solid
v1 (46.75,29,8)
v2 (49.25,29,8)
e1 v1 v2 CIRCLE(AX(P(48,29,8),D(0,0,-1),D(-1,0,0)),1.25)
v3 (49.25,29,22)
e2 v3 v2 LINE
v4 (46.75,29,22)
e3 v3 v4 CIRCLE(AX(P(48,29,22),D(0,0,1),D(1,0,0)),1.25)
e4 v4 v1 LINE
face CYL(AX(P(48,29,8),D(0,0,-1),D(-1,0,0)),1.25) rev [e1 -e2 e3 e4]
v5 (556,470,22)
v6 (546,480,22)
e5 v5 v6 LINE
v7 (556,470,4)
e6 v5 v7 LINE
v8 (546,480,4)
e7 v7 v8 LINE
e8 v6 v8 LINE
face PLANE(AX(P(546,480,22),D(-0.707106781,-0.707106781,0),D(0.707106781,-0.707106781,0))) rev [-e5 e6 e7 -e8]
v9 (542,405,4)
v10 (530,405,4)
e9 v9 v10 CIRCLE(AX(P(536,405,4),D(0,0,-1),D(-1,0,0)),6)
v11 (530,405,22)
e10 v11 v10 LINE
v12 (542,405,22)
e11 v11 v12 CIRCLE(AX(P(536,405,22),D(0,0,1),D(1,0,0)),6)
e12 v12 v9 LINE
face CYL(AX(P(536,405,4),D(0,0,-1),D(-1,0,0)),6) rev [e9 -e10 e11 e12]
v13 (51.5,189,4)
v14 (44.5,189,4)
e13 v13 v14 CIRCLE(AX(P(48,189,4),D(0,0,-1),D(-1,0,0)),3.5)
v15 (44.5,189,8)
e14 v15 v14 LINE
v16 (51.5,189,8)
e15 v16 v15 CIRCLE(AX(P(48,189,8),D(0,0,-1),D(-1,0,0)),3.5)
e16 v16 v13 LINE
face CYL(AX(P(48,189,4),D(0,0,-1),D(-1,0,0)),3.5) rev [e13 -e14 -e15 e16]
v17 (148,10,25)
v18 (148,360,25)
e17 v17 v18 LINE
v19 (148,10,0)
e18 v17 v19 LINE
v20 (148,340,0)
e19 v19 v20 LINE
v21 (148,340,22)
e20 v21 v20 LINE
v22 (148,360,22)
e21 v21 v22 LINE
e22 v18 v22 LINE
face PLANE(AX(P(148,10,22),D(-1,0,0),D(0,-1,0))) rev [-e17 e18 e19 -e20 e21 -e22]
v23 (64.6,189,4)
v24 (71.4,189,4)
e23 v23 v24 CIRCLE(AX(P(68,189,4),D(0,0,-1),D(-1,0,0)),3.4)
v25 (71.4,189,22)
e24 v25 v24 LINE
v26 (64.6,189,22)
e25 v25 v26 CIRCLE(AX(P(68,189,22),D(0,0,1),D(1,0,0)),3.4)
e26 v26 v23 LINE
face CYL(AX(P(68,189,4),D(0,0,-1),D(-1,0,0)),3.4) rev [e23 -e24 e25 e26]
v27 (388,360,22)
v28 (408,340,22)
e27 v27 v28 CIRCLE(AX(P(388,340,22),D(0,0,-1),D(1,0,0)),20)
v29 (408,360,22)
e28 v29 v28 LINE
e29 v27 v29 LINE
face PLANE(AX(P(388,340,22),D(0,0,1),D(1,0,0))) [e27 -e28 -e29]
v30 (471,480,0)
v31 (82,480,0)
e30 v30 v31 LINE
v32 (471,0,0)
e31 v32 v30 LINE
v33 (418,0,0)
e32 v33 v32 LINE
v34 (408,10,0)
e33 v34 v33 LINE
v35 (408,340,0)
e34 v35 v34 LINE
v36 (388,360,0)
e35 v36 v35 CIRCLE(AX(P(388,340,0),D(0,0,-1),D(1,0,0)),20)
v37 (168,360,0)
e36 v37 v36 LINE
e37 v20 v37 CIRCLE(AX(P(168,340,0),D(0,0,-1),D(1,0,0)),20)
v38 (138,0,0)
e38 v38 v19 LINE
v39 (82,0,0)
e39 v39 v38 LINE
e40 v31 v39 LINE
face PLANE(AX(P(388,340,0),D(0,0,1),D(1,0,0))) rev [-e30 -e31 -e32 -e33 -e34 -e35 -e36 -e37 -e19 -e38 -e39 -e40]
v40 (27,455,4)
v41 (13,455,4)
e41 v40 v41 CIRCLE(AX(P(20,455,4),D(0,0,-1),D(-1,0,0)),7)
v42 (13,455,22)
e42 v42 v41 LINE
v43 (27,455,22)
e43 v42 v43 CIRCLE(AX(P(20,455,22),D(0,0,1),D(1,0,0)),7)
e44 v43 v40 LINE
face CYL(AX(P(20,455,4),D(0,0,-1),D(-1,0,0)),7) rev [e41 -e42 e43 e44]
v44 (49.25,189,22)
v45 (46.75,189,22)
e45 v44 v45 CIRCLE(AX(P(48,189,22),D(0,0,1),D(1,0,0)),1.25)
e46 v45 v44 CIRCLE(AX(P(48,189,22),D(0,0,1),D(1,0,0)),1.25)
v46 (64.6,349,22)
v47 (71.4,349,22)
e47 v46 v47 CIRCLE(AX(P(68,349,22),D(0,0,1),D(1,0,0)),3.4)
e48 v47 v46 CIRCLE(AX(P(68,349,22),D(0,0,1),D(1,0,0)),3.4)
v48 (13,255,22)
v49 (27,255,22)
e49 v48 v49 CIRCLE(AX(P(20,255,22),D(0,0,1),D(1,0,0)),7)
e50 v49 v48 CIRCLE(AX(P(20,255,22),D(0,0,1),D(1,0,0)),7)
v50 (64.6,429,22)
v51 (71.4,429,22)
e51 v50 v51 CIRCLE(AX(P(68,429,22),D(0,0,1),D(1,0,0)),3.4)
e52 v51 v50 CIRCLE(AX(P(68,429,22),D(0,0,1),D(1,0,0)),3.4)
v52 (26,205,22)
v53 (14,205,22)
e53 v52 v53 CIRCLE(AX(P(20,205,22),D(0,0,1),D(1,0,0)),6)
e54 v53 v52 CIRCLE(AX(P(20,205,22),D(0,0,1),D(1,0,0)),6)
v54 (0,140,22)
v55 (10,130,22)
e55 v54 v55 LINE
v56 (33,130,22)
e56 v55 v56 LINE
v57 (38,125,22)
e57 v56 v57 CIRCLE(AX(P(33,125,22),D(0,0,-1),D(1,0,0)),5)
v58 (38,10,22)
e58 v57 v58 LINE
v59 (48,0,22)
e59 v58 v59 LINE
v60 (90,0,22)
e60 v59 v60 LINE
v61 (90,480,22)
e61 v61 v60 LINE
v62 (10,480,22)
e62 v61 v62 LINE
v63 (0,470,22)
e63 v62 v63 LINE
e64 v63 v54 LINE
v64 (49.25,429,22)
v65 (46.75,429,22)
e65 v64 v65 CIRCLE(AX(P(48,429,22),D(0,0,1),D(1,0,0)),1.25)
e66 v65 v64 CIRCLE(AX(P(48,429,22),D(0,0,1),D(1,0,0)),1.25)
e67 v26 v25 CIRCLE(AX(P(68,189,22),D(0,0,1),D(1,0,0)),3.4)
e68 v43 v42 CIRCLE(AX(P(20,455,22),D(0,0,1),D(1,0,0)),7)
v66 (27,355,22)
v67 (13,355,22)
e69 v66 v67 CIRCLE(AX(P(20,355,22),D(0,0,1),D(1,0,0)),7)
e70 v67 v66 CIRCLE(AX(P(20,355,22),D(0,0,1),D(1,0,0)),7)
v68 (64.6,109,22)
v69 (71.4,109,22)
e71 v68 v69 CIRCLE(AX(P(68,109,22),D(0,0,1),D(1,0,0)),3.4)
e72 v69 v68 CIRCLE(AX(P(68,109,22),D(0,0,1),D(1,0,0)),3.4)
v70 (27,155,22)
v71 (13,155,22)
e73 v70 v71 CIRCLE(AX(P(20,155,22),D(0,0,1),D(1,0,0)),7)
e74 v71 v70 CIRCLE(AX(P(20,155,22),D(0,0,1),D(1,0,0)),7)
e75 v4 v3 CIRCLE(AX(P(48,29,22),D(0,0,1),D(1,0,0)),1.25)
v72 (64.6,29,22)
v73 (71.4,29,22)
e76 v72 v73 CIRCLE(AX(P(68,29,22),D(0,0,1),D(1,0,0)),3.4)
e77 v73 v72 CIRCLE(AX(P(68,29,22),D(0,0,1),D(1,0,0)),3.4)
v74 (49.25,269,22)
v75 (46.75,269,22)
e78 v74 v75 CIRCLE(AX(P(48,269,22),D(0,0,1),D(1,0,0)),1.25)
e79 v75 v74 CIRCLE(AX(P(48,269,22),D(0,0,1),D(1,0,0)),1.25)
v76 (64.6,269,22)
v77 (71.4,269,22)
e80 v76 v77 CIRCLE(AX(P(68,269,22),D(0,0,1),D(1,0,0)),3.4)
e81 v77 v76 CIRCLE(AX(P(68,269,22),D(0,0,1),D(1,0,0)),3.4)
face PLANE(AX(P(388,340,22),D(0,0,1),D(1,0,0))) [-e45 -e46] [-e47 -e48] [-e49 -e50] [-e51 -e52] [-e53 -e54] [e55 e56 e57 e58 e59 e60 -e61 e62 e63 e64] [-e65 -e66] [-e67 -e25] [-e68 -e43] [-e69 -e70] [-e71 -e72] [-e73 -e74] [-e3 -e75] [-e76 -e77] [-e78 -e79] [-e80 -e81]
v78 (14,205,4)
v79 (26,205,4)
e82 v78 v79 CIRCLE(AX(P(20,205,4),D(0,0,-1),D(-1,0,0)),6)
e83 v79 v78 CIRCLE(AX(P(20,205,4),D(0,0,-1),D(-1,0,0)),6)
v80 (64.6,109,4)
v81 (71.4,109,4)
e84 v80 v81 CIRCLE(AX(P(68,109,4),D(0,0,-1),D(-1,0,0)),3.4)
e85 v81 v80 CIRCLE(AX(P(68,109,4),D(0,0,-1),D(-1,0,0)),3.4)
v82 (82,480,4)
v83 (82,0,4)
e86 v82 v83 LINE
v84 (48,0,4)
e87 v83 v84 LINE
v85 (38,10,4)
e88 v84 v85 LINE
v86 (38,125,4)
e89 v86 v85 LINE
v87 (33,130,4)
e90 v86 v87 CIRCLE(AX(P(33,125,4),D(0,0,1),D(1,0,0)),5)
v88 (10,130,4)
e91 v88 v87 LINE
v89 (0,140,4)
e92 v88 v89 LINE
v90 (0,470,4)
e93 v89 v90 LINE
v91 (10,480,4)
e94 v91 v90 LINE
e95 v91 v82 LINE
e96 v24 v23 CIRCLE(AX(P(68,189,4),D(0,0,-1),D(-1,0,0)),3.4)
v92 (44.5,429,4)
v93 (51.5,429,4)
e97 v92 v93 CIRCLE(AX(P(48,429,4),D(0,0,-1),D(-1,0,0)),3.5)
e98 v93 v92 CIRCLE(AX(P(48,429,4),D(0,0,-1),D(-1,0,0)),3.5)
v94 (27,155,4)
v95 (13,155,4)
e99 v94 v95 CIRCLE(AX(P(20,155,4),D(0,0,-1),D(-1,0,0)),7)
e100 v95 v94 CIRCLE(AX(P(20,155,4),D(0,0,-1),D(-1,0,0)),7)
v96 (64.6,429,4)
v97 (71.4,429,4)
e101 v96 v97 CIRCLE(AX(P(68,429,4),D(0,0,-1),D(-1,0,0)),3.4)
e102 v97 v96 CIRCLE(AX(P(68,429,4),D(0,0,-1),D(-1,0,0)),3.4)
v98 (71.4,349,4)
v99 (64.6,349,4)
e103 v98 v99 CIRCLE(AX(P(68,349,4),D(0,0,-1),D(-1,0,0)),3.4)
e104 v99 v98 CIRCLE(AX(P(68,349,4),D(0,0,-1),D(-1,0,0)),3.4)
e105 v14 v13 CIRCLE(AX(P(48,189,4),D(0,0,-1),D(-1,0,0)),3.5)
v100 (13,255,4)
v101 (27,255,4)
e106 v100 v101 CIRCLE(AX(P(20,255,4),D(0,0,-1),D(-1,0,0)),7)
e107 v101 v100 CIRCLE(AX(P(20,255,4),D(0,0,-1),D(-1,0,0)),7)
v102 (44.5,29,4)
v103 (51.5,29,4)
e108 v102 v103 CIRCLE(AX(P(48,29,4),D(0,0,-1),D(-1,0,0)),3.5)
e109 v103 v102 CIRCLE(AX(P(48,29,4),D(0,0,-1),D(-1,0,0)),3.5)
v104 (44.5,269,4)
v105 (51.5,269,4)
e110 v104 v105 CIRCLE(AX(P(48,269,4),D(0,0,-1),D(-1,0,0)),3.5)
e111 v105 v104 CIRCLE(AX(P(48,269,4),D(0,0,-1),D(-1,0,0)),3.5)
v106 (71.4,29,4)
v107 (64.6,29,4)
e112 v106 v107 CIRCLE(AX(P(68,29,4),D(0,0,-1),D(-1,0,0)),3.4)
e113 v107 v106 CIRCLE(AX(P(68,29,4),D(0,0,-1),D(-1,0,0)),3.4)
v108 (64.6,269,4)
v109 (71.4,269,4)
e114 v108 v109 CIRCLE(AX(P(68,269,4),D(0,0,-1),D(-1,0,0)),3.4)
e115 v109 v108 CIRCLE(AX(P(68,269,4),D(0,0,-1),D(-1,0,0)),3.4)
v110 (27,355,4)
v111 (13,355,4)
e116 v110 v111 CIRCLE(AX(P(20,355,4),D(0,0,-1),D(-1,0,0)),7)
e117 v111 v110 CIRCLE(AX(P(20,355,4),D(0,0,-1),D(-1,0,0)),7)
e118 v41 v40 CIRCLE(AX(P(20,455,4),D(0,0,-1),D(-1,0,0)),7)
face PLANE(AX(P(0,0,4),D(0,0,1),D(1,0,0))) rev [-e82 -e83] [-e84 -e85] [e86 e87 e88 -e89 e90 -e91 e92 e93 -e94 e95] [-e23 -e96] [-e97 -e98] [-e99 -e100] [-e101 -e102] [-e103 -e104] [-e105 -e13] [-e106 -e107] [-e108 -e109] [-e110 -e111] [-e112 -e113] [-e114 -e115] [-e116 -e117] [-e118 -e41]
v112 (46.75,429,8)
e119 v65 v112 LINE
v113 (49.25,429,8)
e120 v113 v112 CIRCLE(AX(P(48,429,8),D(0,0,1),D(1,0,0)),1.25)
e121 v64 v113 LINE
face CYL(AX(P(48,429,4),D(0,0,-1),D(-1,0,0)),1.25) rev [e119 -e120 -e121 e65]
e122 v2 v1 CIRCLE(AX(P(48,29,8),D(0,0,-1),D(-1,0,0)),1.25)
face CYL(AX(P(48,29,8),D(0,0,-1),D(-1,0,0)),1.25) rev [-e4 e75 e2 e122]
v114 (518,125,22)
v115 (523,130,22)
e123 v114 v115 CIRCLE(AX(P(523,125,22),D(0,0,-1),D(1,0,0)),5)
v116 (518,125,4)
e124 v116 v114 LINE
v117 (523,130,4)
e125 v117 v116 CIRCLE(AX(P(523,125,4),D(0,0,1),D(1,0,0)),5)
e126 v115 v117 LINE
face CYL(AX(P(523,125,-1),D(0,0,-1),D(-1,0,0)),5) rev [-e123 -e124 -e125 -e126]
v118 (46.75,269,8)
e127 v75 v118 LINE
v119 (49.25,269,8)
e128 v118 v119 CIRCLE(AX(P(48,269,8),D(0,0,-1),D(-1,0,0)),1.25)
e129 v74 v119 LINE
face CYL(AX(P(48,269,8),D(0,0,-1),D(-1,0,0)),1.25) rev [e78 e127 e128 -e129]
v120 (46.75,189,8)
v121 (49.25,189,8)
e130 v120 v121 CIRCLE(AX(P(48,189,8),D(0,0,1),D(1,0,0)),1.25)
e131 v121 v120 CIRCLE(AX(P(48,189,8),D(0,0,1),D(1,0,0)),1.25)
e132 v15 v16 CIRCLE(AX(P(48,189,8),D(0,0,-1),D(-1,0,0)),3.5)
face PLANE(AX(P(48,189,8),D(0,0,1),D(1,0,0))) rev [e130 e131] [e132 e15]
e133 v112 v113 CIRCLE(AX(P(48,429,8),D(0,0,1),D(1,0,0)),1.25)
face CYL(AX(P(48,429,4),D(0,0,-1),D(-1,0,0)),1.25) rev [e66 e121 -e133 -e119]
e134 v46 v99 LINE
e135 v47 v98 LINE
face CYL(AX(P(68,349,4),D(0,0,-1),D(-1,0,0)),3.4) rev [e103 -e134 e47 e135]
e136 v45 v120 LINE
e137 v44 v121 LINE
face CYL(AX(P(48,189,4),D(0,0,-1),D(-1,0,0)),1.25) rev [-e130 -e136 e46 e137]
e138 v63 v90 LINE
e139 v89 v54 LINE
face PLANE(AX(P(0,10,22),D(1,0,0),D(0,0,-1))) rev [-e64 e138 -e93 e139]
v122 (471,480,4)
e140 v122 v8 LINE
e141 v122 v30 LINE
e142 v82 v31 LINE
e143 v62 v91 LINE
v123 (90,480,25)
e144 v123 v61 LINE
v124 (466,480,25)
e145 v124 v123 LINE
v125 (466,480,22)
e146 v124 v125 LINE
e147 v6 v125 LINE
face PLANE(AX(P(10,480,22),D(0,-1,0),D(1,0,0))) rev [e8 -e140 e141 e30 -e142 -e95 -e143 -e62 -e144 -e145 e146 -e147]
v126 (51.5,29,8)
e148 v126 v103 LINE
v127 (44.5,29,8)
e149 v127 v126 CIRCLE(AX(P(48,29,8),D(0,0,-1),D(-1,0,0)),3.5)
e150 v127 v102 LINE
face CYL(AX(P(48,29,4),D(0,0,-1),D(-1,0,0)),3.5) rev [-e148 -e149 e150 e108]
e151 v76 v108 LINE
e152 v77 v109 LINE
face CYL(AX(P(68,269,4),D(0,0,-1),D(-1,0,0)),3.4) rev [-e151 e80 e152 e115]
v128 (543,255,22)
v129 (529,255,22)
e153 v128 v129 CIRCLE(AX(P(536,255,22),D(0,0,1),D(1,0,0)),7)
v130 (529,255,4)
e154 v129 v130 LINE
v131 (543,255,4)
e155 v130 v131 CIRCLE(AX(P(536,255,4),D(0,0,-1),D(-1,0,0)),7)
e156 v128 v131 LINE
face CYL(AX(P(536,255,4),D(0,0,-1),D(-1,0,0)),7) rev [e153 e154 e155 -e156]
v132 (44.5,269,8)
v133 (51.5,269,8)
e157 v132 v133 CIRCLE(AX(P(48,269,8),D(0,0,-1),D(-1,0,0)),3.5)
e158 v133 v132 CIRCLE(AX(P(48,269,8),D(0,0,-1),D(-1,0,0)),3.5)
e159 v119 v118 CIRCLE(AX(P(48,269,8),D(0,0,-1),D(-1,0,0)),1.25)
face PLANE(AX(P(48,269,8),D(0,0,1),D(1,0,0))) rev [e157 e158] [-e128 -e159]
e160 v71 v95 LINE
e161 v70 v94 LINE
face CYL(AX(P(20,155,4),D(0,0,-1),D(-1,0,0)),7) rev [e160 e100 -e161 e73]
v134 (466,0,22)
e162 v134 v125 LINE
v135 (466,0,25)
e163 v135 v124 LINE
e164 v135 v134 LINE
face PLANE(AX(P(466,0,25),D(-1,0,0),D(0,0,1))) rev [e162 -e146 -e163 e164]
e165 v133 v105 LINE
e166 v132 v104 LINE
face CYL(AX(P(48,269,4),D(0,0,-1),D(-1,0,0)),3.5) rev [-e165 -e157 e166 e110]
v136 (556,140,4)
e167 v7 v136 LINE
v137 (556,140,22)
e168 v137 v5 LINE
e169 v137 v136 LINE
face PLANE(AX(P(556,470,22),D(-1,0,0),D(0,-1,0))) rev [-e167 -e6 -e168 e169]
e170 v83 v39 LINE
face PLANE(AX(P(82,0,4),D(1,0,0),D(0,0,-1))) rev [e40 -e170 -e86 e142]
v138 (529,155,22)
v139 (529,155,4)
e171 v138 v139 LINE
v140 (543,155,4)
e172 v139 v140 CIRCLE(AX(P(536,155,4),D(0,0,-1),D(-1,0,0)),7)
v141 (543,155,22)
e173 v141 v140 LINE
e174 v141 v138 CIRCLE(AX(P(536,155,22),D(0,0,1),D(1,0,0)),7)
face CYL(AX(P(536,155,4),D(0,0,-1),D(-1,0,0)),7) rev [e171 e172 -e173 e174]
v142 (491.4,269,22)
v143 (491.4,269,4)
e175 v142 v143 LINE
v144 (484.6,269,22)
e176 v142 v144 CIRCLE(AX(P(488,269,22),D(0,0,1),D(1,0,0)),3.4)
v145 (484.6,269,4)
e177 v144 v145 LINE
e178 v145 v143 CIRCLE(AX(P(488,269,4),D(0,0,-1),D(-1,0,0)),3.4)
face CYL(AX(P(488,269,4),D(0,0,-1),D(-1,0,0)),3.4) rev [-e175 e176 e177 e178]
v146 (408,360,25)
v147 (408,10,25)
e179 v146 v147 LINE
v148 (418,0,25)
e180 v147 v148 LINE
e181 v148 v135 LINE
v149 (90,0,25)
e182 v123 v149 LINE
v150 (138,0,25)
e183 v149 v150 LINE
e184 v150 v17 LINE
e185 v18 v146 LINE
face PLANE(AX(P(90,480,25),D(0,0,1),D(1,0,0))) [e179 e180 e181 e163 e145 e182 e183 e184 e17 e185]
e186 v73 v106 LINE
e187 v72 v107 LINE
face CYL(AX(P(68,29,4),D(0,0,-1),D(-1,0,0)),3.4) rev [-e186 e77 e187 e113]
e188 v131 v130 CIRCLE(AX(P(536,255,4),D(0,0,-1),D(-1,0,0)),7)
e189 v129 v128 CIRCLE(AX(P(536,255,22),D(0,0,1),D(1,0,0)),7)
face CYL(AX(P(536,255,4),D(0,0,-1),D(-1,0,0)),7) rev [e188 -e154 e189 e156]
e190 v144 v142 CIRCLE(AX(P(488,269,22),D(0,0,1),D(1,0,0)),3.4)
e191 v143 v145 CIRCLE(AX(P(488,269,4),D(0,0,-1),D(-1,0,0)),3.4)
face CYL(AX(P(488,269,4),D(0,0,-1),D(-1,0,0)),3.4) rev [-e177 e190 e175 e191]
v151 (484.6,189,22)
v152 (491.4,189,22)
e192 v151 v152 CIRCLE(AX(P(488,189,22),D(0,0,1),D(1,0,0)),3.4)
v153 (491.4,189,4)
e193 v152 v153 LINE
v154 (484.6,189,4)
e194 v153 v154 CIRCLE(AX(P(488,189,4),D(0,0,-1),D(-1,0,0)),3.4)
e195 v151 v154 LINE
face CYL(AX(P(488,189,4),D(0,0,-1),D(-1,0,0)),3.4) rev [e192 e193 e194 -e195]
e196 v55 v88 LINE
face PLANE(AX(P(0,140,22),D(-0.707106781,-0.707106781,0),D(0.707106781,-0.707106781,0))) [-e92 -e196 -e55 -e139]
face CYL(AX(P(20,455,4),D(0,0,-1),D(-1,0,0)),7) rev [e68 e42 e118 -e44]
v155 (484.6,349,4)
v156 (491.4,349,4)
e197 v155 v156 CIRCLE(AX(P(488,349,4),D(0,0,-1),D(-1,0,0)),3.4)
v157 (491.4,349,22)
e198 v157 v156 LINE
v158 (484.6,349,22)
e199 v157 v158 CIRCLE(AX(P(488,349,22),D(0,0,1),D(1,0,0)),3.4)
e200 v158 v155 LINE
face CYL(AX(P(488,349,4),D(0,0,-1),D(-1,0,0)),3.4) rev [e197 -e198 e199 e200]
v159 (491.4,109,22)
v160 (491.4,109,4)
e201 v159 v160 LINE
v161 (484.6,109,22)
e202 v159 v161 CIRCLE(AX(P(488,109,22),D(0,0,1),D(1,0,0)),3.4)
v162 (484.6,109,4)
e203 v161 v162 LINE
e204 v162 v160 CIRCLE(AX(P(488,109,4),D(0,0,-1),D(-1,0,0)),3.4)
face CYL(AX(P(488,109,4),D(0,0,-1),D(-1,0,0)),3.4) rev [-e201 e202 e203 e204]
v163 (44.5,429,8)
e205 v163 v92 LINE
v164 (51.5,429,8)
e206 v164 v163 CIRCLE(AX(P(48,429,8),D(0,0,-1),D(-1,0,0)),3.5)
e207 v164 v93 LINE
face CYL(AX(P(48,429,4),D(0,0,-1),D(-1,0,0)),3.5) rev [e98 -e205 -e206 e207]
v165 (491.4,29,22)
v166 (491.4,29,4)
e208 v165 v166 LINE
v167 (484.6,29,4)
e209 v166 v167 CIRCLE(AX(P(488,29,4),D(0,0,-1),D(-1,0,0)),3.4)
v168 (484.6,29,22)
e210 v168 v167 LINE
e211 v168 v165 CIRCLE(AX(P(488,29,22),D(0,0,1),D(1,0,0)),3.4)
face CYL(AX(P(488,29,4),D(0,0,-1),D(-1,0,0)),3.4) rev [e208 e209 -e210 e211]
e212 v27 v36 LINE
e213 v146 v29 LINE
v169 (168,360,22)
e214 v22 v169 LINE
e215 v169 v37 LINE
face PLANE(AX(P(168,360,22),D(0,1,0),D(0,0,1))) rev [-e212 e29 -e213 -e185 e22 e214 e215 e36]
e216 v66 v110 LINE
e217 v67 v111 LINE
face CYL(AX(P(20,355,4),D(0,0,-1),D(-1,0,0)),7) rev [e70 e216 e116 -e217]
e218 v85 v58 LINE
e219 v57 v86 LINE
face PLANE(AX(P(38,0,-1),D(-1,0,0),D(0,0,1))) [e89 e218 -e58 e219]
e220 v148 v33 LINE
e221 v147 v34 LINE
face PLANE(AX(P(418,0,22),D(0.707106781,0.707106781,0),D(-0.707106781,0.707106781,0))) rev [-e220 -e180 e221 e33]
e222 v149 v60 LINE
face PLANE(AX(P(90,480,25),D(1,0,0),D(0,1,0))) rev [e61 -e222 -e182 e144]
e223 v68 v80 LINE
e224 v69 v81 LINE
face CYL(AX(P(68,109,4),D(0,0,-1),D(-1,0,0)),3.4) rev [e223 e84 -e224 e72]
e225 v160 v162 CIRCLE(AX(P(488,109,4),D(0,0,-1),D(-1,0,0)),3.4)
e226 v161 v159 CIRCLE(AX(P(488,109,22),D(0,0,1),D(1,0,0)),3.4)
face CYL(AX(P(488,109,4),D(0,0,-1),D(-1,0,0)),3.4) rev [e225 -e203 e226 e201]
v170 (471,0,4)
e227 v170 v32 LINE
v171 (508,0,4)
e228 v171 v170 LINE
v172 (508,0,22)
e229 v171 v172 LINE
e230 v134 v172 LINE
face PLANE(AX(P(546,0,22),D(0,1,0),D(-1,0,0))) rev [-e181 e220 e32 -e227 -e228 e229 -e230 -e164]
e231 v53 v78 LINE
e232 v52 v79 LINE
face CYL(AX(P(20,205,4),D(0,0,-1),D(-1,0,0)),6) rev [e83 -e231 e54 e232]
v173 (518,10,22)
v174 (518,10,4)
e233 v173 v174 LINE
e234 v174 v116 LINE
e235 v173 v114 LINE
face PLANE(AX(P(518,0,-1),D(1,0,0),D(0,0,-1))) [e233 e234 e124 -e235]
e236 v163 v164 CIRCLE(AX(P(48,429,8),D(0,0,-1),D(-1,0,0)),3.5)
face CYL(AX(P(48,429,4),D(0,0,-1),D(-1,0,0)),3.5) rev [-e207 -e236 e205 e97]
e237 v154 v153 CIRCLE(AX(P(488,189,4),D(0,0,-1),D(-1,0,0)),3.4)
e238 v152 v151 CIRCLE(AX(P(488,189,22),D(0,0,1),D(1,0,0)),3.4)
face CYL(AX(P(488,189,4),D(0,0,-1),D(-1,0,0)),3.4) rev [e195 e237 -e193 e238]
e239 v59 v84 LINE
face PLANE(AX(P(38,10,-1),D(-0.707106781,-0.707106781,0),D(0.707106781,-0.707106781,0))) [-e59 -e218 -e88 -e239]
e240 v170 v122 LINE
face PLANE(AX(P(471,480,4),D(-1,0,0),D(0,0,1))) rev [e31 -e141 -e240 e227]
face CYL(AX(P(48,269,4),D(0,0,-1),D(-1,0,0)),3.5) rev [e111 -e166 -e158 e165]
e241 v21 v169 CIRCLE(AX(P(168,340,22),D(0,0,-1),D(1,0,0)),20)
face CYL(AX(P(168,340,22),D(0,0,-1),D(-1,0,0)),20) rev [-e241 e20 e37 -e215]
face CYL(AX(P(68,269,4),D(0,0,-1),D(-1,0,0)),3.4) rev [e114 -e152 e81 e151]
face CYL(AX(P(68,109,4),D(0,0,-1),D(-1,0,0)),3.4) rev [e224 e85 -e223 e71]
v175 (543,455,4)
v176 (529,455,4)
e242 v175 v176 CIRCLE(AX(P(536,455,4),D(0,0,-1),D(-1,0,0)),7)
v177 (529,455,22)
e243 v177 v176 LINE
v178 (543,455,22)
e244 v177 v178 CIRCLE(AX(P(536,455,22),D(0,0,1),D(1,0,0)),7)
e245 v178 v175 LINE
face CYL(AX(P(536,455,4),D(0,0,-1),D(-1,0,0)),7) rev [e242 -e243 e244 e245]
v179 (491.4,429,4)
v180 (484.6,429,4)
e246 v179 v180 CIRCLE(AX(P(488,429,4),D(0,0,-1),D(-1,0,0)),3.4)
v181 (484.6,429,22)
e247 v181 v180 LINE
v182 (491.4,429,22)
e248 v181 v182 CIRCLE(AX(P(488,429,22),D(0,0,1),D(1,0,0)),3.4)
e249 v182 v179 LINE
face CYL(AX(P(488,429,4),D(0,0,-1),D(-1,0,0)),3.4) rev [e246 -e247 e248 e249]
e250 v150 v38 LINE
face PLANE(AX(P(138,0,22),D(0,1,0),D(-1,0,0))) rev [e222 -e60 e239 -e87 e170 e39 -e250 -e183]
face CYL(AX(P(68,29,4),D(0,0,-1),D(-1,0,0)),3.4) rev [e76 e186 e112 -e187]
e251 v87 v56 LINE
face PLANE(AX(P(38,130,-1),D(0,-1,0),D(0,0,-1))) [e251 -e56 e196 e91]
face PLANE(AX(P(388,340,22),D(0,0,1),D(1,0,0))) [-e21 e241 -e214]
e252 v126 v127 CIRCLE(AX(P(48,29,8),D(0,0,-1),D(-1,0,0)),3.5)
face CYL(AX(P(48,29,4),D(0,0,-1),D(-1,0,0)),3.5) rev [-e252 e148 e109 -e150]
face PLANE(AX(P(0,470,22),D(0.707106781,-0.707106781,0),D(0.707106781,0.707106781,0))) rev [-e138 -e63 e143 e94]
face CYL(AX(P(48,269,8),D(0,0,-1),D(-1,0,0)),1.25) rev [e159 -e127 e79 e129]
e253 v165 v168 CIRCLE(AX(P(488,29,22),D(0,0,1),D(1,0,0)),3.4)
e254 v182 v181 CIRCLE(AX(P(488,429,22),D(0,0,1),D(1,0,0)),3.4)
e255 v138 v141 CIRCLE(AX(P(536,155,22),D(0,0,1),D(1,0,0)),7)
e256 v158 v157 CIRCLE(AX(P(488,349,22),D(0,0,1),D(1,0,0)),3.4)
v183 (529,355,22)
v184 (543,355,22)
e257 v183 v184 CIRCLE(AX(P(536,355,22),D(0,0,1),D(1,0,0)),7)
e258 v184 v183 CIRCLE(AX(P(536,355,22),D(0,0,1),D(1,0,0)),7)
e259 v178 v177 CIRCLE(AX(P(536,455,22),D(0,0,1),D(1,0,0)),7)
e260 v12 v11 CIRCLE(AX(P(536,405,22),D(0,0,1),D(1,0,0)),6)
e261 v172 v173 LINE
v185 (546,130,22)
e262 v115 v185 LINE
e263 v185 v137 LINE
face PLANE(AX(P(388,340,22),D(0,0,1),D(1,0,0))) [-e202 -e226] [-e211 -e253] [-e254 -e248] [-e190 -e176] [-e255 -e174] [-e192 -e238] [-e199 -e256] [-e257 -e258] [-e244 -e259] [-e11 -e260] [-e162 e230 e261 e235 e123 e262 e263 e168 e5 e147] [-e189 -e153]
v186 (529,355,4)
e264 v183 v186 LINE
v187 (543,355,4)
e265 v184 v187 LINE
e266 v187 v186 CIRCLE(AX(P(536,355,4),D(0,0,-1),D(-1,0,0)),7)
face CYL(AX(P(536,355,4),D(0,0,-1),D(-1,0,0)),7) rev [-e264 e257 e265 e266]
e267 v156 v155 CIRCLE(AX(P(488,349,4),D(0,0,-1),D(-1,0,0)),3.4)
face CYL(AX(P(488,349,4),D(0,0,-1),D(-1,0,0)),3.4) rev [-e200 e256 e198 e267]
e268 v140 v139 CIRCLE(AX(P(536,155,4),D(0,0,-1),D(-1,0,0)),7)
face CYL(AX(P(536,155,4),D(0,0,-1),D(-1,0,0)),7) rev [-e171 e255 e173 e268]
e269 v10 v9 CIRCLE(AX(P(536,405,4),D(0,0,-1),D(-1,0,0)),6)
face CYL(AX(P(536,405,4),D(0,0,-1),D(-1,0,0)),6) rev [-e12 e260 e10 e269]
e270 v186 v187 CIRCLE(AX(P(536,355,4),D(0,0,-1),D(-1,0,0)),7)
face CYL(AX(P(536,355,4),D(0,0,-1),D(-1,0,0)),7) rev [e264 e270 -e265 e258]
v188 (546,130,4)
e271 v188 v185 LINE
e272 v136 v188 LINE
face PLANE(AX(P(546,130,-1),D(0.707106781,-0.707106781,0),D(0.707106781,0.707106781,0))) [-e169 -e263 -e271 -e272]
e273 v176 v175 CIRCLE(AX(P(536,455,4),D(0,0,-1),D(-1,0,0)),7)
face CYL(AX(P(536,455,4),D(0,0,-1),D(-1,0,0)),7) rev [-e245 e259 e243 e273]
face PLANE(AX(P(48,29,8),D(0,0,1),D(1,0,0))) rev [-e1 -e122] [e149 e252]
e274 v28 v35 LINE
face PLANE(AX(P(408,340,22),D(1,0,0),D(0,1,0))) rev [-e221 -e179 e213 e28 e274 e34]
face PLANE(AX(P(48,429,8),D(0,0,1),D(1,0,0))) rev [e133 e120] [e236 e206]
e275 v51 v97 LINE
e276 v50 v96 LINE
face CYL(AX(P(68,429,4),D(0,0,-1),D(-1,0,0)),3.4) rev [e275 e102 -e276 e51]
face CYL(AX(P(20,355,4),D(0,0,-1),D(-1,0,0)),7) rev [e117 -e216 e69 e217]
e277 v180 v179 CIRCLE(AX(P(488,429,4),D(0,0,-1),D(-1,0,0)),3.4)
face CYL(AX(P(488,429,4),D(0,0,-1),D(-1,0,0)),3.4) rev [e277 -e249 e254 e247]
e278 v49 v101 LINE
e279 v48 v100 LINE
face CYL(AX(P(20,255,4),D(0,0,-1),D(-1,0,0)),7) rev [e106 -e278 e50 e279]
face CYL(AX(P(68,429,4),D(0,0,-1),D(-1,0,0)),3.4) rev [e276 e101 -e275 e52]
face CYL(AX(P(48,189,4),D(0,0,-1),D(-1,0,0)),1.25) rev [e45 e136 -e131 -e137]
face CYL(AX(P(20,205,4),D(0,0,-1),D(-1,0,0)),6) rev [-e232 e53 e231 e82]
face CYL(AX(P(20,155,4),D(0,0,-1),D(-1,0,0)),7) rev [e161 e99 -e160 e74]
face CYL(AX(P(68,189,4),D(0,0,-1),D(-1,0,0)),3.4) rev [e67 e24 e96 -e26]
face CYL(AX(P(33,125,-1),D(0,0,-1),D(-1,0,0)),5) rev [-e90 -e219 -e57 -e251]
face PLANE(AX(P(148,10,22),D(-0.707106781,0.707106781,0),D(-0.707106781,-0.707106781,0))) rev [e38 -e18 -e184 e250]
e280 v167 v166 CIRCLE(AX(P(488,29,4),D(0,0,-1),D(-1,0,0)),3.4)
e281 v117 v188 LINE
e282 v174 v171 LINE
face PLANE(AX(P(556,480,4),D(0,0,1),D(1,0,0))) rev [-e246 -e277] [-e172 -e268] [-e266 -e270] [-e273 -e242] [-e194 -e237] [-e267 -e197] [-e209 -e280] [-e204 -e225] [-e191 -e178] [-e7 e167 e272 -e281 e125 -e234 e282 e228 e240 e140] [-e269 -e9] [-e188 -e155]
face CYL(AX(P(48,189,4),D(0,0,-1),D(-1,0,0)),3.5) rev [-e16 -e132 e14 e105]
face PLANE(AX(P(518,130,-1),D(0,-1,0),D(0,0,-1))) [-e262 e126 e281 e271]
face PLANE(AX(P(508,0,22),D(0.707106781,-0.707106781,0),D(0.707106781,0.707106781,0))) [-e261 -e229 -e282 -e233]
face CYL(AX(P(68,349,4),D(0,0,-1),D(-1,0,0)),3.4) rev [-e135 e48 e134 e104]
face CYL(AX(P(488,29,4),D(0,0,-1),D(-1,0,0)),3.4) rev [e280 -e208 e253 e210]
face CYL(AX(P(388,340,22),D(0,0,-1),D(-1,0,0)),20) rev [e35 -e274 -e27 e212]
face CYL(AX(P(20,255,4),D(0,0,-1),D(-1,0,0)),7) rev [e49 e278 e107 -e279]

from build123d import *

# Parameters (mm, degrees)
BOSS_EXTRUDE1_DEPTH             = 22
SKETCH2_W                       = 85
SKETCH2_H                       = 480
SKETCH2_W_2                     = 82
CUT_EXTRUDE1_DEPTH              = 4
M8_TAPPED_HOLE1_AT_2_COUNT      = 2
M8_TAPPED_HOLE1_AT_2_PITCH      = 80
M8_TAPPED_HOLE1_AT_3_COUNT      = 2
M8_TAPPED_HOLE1_AT_3_PITCH      = 160
M8_TAPPED_HOLE1_AT_4_COUNT      = 2
M8_TAPPED_HOLE1_AT_4_PITCH      = 240
M8_TAPPED_HOLE1_AT_5_COUNT      = 2
M8_TAPPED_HOLE1_AT_5_PITCH      = 320
M8_TAPPED_HOLE1_AT_6_COUNT      = 2
M8_TAPPED_HOLE1_AT_6_PITCH      = 80
F_14_0_14_DIAMETER_HOLE1_D      = 14
F_7_0_7_DIAMETER_HOLE1_D        = 7
F_7_0_7_DIAMETER_HOLE1_DEPTH    = 4
M3_TAPPED_HOLE1_D               = 2.5
M3_TAPPED_HOLE1_DEPTH           = 18
M3_TAPPED_HOLE1_ON_FACE_2_D     = 2.5
M3_TAPPED_HOLE1_ON_FACE_2_DEPTH = 18
F_12_0_12_DIAMETER_HOLE1_D      = 12
CUT_EXTRUDE2_REACH              = 736.752
SKETCH9_W                       = 38
SKETCH9_H                       = 130
CUT_EXTRUDE2_DIRECTION_2_DEPTH  = 5
FILLET1_R                       = 5
CHAMFER1_SIZE                   = 10
BOSS_EXTRUDE2_DEPTH             = 3


with BuildPart() as part:
    # Sketch1 → Boss-Extrude1 (new body)
    with BuildSketch(Plane.XY):
        with BuildLine():
            Line((0, 10), (0, 470))
            Line((0, 470), (10, 480))
            Line((10, 480), (546, 480))
            Line((546, 480), (556, 470))
            Line((556, 470), (556, 10))
            Line((556, 10), (546, 0))
            Line((546, 0), (418, 0))
            Line((418, 0), (408, 10))
            Line((408, 10), (408, 340))
            ThreePointArc((408, 340), (402.142135624, 354.142135624), (388, 360))
            Line((388, 360), (168, 360))
            ThreePointArc((168, 360), (153.857864376, 354.142135624), (148, 340))
            Line((148, 340), (148, 10))
            Line((148, 10), (138, 0))
            Line((138, 0), (10, 0))
            Line((10, 0), (0, 10))
        make_face()
    extrude(amount=BOSS_EXTRUDE1_DEPTH)

    # Sketch2 → Cut-Extrude1 (cut)
    with BuildSketch(Plane(origin=(0, 0, 0), x_dir=(-1, 0, 0), z_dir=(0, 0, -1))):
        with Locations((-513.5, 240)):
            Rectangle(SKETCH2_W, SKETCH2_H)
        with Locations((-41, 240)):
            Rectangle(SKETCH2_W_2, SKETCH2_H)
    extrude(amount=-CUT_EXTRUDE1_DEPTH, mode=Mode.SUBTRACT)

    # Sketch3 → M8 Tapped Hole1 (revolve, cut)
    with BuildSketch(Plane(origin=(488, 349, 4), x_dir=(0, 1, 0), z_dir=(1, 0, 0))):
        Polygon((0, 0), (0, 21.712990915), (3.4, 19.75), (3.4, 0), align=None)
    m8_tapped_hole1 = revolve(axis=Axis((488, 349, -2.35), (0, 0, 1)), mode=Mode.SUBTRACT)

    # M8 Tapped Hole1 at 2: M8 Tapped Hole1 ×2
    with Locations(*[(0, -i * M8_TAPPED_HOLE1_AT_2_PITCH, 0) for i in range(1, M8_TAPPED_HOLE1_AT_2_COUNT)]):
        add(m8_tapped_hole1, mode=Mode.SUBTRACT)

    # M8 Tapped Hole1 at 3: M8 Tapped Hole1 ×2
    with Locations(*[(0, -i * M8_TAPPED_HOLE1_AT_3_PITCH, 0) for i in range(1, M8_TAPPED_HOLE1_AT_3_COUNT)]):
        add(m8_tapped_hole1, mode=Mode.SUBTRACT)

    # M8 Tapped Hole1 at 4: M8 Tapped Hole1 ×2
    with Locations(*[(0, -i * M8_TAPPED_HOLE1_AT_4_PITCH, 0) for i in range(1, M8_TAPPED_HOLE1_AT_4_COUNT)]):
        add(m8_tapped_hole1, mode=Mode.SUBTRACT)

    # M8 Tapped Hole1 at 5: M8 Tapped Hole1 ×2
    with Locations(*[(0, -i * M8_TAPPED_HOLE1_AT_5_PITCH, 0) for i in range(1, M8_TAPPED_HOLE1_AT_5_COUNT)]):
        add(m8_tapped_hole1, mode=Mode.SUBTRACT)

    # M8 Tapped Hole1 at 6: M8 Tapped Hole1 ×2
    with Locations(*[(0, i * M8_TAPPED_HOLE1_AT_6_PITCH, 0) for i in range(1, M8_TAPPED_HOLE1_AT_6_COUNT)]):
        add(m8_tapped_hole1, mode=Mode.SUBTRACT)

    # Mirror1: M8 Tapped Hole1 across plane
    add(m8_tapped_hole1.mirror(Plane(origin=(278, 0, 0), x_dir=(0, 0, 1), z_dir=(1, 0, 0))), mode=Mode.SUBTRACT)

    # Mirror1 copy 1 sketch → Mirror1 copy 1 (revolve, cut)
    with BuildSketch(Plane(origin=(68, 269, 4), x_dir=(0, 1, 0), z_dir=(-1, 0, 0))):
        Polygon((0, 0), (0, -21.712990915), (3.4, -19.75), (3.4, 0), align=None)
    revolve(axis=Axis((68, 269, -2.35), (0, 0, -1)), mode=Mode.SUBTRACT)

    # Mirror1 copy 2 sketch → Mirror1 copy 2 (revolve, cut)
    with BuildSketch(Plane(origin=(68, 189, 4), x_dir=(0, 1, 0), z_dir=(-1, 0, 0))):
        Polygon((0, 0), (0, -21.712990915), (3.4, -19.75), (3.4, 0), align=None)
    revolve(axis=Axis((68, 189, -2.35), (0, 0, -1)), mode=Mode.SUBTRACT)

    # Mirror1 copy 3 sketch → Mirror1 copy 3 (revolve, cut)
    with BuildSketch(Plane(origin=(68, 109, 4), x_dir=(0, 1, 0), z_dir=(-1, 0, 0))):
        Polygon((0, 0), (0, -21.712990915), (3.4, -19.75), (3.4, 0), align=None)
    revolve(axis=Axis((68, 109, -2.35), (0, 0, -1)), mode=Mode.SUBTRACT)

    # Mirror1 copy 4 sketch → Mirror1 copy 4 (revolve, cut)
    with BuildSketch(Plane(origin=(68, 29, 4), x_dir=(0, 1, 0), z_dir=(-1, 0, 0))):
        Polygon((0, 0), (0, -21.712990915), (3.4, -19.75), (3.4, 0), align=None)
    revolve(axis=Axis((68, 29, -2.35), (0, 0, -1)), mode=Mode.SUBTRACT)

    # Mirror1 copy 5 sketch → Mirror1 copy 5 (revolve, cut)
    with BuildSketch(Plane(origin=(68, 429, 4), x_dir=(0, 1, 0), z_dir=(-1, 0, 0))):
        Polygon((0, 0), (0, -21.712990915), (3.4, -19.75), (3.4, 0), align=None)
    revolve(axis=Axis((68, 429, -2.35), (0, 0, -1)), mode=Mode.SUBTRACT)

    # Ø14.0 (14) Diameter Hole1 (through all)
    with Locations(Plane(origin=(536, 455, 4), x_dir=(-1, 0, 0), z_dir=(0, 0, -1))):
        with Locations((0, 0), (0, -100), (0, -200), (0, -300)):
            f_14_0_14_diameter_hole1 = Hole(F_14_0_14_DIAMETER_HOLE1_D / 2)

    # Mirror2: Ø14.0 (14) Diameter Hole1 across plane
    add(f_14_0_14_diameter_hole1.mirror(Plane.ZY.offset(-278)), mode=Mode.SUBTRACT)

    # Ø7.0 (7) Diameter Hole1
    with Locations(Plane(origin=(48, 429, 4), x_dir=(-1, 0, 0), z_dir=(0, 0, -1))):
        with Locations((0, 0), (0, -160), (0, -240), (0, -400)):
            Hole(F_7_0_7_DIAMETER_HOLE1_D / 2, depth=F_7_0_7_DIAMETER_HOLE1_DEPTH)

    # M3 Tapped Hole1
    with Locations(Plane(origin=(48, 429, 4), x_dir=(-1, 0, 0), z_dir=(0, 0, -1))):
        with Locations((0, 0), (0, -240)):
            Hole(M3_TAPPED_HOLE1_D / 2, depth=M3_TAPPED_HOLE1_DEPTH)

    # M3 Tapped Hole1 on face 2
    with Locations(Plane(origin=(48, 269, 8), x_dir=(-1, 0, 0), z_dir=(0, 0, -1))):
        with Locations((0, 0), (0, -240)):
            Hole(M3_TAPPED_HOLE1_ON_FACE_2_D / 2, depth=M3_TAPPED_HOLE1_ON_FACE_2_DEPTH)

    # Ø12.0 (12) Diameter Hole1 (through all)
    with Locations(Plane(origin=(20, 205, 4), x_dir=(-1, 0, 0), z_dir=(0, 0, -1))):
        with Locations((0, 0), (-516, 200)):
            Hole(F_12_0_12_DIAMETER_HOLE1_D / 2)

    # Sketch9 → Cut-Extrude2 (cut, up to next)
    with BuildSketch(Plane(origin=(0, 0, 4), x_dir=(-1, 0, 0), z_dir=(0, 0, -1)), mode=Mode.PRIVATE) as cut_extrude2_sk1:
        with Locations((-537, 65)):
            Rectangle(SKETCH9_W, SKETCH9_H)
    cut_extrude2_tool1 = extrude(cut_extrude2_sk1.sketch, amount=-CUT_EXTRUDE2_REACH, mode=Mode.PRIVATE) & part.part
    # Sketch9 → Cut-Extrude2 (cut, up to next)
    with BuildSketch(Plane(origin=(0, 0, 4), x_dir=(-1, 0, 0), z_dir=(0, 0, -1)), mode=Mode.PRIVATE) as cut_extrude2_sk2:
        with Locations((-19, 65)):
            Rectangle(SKETCH9_W, SKETCH9_H)
    cut_extrude2_tool2 = extrude(cut_extrude2_sk2.sketch, amount=-CUT_EXTRUDE2_REACH, mode=Mode.PRIVATE) & part.part
    add(cut_extrude2_tool1.solids().sort_by_distance((537, 65, 4))[0], mode=Mode.SUBTRACT)
    add(cut_extrude2_tool2.solids().sort_by_distance((19, 65, 4))[0], mode=Mode.SUBTRACT)

    # Sketch9 → Cut-Extrude2 direction 2 (cut)
    with BuildSketch(Plane(origin=(0, 0, 4), x_dir=(-1, 0, 0), z_dir=(0, 0, -1))):
        with Locations((-537, 65)):
            Rectangle(SKETCH9_W, SKETCH9_H)
        with Locations((-19, 65)):
            Rectangle(SKETCH9_W, SKETCH9_H)
    extrude(amount=CUT_EXTRUDE2_DIRECTION_2_DEPTH, mode=Mode.SUBTRACT)

    # Fillet1
    fillet1_edges = [part.edges().sort_by_distance(p)[0] for p in [
        (518, 130, 13),
        (38, 130, 13),
    ]]
    fillet(fillet1_edges, radius=FILLET1_R)

    # Chamfer1
    chamfer1_edges = [part.edges().sort_by_distance(p)[0] for p in [
        (556, 130, 13),
        (518, 0, 13),
        (38, 0, 13),
        (0, 130, 13),
    ]]
    chamfer(chamfer1_edges, length=CHAMFER1_SIZE)

    # Sketch10 → Boss-Extrude2 (add)
    with BuildSketch(Plane.XY.offset(22)):
        Polygon((90, 480), (90, 0), (138, 0), (148, 10), (148, 360), (408, 360), (408, 10), (418, 0), (466, 0), (466, 480), align=None)
    extrude(amount=BOSS_EXTRUDE2_DEPTH)


solid = part.part
